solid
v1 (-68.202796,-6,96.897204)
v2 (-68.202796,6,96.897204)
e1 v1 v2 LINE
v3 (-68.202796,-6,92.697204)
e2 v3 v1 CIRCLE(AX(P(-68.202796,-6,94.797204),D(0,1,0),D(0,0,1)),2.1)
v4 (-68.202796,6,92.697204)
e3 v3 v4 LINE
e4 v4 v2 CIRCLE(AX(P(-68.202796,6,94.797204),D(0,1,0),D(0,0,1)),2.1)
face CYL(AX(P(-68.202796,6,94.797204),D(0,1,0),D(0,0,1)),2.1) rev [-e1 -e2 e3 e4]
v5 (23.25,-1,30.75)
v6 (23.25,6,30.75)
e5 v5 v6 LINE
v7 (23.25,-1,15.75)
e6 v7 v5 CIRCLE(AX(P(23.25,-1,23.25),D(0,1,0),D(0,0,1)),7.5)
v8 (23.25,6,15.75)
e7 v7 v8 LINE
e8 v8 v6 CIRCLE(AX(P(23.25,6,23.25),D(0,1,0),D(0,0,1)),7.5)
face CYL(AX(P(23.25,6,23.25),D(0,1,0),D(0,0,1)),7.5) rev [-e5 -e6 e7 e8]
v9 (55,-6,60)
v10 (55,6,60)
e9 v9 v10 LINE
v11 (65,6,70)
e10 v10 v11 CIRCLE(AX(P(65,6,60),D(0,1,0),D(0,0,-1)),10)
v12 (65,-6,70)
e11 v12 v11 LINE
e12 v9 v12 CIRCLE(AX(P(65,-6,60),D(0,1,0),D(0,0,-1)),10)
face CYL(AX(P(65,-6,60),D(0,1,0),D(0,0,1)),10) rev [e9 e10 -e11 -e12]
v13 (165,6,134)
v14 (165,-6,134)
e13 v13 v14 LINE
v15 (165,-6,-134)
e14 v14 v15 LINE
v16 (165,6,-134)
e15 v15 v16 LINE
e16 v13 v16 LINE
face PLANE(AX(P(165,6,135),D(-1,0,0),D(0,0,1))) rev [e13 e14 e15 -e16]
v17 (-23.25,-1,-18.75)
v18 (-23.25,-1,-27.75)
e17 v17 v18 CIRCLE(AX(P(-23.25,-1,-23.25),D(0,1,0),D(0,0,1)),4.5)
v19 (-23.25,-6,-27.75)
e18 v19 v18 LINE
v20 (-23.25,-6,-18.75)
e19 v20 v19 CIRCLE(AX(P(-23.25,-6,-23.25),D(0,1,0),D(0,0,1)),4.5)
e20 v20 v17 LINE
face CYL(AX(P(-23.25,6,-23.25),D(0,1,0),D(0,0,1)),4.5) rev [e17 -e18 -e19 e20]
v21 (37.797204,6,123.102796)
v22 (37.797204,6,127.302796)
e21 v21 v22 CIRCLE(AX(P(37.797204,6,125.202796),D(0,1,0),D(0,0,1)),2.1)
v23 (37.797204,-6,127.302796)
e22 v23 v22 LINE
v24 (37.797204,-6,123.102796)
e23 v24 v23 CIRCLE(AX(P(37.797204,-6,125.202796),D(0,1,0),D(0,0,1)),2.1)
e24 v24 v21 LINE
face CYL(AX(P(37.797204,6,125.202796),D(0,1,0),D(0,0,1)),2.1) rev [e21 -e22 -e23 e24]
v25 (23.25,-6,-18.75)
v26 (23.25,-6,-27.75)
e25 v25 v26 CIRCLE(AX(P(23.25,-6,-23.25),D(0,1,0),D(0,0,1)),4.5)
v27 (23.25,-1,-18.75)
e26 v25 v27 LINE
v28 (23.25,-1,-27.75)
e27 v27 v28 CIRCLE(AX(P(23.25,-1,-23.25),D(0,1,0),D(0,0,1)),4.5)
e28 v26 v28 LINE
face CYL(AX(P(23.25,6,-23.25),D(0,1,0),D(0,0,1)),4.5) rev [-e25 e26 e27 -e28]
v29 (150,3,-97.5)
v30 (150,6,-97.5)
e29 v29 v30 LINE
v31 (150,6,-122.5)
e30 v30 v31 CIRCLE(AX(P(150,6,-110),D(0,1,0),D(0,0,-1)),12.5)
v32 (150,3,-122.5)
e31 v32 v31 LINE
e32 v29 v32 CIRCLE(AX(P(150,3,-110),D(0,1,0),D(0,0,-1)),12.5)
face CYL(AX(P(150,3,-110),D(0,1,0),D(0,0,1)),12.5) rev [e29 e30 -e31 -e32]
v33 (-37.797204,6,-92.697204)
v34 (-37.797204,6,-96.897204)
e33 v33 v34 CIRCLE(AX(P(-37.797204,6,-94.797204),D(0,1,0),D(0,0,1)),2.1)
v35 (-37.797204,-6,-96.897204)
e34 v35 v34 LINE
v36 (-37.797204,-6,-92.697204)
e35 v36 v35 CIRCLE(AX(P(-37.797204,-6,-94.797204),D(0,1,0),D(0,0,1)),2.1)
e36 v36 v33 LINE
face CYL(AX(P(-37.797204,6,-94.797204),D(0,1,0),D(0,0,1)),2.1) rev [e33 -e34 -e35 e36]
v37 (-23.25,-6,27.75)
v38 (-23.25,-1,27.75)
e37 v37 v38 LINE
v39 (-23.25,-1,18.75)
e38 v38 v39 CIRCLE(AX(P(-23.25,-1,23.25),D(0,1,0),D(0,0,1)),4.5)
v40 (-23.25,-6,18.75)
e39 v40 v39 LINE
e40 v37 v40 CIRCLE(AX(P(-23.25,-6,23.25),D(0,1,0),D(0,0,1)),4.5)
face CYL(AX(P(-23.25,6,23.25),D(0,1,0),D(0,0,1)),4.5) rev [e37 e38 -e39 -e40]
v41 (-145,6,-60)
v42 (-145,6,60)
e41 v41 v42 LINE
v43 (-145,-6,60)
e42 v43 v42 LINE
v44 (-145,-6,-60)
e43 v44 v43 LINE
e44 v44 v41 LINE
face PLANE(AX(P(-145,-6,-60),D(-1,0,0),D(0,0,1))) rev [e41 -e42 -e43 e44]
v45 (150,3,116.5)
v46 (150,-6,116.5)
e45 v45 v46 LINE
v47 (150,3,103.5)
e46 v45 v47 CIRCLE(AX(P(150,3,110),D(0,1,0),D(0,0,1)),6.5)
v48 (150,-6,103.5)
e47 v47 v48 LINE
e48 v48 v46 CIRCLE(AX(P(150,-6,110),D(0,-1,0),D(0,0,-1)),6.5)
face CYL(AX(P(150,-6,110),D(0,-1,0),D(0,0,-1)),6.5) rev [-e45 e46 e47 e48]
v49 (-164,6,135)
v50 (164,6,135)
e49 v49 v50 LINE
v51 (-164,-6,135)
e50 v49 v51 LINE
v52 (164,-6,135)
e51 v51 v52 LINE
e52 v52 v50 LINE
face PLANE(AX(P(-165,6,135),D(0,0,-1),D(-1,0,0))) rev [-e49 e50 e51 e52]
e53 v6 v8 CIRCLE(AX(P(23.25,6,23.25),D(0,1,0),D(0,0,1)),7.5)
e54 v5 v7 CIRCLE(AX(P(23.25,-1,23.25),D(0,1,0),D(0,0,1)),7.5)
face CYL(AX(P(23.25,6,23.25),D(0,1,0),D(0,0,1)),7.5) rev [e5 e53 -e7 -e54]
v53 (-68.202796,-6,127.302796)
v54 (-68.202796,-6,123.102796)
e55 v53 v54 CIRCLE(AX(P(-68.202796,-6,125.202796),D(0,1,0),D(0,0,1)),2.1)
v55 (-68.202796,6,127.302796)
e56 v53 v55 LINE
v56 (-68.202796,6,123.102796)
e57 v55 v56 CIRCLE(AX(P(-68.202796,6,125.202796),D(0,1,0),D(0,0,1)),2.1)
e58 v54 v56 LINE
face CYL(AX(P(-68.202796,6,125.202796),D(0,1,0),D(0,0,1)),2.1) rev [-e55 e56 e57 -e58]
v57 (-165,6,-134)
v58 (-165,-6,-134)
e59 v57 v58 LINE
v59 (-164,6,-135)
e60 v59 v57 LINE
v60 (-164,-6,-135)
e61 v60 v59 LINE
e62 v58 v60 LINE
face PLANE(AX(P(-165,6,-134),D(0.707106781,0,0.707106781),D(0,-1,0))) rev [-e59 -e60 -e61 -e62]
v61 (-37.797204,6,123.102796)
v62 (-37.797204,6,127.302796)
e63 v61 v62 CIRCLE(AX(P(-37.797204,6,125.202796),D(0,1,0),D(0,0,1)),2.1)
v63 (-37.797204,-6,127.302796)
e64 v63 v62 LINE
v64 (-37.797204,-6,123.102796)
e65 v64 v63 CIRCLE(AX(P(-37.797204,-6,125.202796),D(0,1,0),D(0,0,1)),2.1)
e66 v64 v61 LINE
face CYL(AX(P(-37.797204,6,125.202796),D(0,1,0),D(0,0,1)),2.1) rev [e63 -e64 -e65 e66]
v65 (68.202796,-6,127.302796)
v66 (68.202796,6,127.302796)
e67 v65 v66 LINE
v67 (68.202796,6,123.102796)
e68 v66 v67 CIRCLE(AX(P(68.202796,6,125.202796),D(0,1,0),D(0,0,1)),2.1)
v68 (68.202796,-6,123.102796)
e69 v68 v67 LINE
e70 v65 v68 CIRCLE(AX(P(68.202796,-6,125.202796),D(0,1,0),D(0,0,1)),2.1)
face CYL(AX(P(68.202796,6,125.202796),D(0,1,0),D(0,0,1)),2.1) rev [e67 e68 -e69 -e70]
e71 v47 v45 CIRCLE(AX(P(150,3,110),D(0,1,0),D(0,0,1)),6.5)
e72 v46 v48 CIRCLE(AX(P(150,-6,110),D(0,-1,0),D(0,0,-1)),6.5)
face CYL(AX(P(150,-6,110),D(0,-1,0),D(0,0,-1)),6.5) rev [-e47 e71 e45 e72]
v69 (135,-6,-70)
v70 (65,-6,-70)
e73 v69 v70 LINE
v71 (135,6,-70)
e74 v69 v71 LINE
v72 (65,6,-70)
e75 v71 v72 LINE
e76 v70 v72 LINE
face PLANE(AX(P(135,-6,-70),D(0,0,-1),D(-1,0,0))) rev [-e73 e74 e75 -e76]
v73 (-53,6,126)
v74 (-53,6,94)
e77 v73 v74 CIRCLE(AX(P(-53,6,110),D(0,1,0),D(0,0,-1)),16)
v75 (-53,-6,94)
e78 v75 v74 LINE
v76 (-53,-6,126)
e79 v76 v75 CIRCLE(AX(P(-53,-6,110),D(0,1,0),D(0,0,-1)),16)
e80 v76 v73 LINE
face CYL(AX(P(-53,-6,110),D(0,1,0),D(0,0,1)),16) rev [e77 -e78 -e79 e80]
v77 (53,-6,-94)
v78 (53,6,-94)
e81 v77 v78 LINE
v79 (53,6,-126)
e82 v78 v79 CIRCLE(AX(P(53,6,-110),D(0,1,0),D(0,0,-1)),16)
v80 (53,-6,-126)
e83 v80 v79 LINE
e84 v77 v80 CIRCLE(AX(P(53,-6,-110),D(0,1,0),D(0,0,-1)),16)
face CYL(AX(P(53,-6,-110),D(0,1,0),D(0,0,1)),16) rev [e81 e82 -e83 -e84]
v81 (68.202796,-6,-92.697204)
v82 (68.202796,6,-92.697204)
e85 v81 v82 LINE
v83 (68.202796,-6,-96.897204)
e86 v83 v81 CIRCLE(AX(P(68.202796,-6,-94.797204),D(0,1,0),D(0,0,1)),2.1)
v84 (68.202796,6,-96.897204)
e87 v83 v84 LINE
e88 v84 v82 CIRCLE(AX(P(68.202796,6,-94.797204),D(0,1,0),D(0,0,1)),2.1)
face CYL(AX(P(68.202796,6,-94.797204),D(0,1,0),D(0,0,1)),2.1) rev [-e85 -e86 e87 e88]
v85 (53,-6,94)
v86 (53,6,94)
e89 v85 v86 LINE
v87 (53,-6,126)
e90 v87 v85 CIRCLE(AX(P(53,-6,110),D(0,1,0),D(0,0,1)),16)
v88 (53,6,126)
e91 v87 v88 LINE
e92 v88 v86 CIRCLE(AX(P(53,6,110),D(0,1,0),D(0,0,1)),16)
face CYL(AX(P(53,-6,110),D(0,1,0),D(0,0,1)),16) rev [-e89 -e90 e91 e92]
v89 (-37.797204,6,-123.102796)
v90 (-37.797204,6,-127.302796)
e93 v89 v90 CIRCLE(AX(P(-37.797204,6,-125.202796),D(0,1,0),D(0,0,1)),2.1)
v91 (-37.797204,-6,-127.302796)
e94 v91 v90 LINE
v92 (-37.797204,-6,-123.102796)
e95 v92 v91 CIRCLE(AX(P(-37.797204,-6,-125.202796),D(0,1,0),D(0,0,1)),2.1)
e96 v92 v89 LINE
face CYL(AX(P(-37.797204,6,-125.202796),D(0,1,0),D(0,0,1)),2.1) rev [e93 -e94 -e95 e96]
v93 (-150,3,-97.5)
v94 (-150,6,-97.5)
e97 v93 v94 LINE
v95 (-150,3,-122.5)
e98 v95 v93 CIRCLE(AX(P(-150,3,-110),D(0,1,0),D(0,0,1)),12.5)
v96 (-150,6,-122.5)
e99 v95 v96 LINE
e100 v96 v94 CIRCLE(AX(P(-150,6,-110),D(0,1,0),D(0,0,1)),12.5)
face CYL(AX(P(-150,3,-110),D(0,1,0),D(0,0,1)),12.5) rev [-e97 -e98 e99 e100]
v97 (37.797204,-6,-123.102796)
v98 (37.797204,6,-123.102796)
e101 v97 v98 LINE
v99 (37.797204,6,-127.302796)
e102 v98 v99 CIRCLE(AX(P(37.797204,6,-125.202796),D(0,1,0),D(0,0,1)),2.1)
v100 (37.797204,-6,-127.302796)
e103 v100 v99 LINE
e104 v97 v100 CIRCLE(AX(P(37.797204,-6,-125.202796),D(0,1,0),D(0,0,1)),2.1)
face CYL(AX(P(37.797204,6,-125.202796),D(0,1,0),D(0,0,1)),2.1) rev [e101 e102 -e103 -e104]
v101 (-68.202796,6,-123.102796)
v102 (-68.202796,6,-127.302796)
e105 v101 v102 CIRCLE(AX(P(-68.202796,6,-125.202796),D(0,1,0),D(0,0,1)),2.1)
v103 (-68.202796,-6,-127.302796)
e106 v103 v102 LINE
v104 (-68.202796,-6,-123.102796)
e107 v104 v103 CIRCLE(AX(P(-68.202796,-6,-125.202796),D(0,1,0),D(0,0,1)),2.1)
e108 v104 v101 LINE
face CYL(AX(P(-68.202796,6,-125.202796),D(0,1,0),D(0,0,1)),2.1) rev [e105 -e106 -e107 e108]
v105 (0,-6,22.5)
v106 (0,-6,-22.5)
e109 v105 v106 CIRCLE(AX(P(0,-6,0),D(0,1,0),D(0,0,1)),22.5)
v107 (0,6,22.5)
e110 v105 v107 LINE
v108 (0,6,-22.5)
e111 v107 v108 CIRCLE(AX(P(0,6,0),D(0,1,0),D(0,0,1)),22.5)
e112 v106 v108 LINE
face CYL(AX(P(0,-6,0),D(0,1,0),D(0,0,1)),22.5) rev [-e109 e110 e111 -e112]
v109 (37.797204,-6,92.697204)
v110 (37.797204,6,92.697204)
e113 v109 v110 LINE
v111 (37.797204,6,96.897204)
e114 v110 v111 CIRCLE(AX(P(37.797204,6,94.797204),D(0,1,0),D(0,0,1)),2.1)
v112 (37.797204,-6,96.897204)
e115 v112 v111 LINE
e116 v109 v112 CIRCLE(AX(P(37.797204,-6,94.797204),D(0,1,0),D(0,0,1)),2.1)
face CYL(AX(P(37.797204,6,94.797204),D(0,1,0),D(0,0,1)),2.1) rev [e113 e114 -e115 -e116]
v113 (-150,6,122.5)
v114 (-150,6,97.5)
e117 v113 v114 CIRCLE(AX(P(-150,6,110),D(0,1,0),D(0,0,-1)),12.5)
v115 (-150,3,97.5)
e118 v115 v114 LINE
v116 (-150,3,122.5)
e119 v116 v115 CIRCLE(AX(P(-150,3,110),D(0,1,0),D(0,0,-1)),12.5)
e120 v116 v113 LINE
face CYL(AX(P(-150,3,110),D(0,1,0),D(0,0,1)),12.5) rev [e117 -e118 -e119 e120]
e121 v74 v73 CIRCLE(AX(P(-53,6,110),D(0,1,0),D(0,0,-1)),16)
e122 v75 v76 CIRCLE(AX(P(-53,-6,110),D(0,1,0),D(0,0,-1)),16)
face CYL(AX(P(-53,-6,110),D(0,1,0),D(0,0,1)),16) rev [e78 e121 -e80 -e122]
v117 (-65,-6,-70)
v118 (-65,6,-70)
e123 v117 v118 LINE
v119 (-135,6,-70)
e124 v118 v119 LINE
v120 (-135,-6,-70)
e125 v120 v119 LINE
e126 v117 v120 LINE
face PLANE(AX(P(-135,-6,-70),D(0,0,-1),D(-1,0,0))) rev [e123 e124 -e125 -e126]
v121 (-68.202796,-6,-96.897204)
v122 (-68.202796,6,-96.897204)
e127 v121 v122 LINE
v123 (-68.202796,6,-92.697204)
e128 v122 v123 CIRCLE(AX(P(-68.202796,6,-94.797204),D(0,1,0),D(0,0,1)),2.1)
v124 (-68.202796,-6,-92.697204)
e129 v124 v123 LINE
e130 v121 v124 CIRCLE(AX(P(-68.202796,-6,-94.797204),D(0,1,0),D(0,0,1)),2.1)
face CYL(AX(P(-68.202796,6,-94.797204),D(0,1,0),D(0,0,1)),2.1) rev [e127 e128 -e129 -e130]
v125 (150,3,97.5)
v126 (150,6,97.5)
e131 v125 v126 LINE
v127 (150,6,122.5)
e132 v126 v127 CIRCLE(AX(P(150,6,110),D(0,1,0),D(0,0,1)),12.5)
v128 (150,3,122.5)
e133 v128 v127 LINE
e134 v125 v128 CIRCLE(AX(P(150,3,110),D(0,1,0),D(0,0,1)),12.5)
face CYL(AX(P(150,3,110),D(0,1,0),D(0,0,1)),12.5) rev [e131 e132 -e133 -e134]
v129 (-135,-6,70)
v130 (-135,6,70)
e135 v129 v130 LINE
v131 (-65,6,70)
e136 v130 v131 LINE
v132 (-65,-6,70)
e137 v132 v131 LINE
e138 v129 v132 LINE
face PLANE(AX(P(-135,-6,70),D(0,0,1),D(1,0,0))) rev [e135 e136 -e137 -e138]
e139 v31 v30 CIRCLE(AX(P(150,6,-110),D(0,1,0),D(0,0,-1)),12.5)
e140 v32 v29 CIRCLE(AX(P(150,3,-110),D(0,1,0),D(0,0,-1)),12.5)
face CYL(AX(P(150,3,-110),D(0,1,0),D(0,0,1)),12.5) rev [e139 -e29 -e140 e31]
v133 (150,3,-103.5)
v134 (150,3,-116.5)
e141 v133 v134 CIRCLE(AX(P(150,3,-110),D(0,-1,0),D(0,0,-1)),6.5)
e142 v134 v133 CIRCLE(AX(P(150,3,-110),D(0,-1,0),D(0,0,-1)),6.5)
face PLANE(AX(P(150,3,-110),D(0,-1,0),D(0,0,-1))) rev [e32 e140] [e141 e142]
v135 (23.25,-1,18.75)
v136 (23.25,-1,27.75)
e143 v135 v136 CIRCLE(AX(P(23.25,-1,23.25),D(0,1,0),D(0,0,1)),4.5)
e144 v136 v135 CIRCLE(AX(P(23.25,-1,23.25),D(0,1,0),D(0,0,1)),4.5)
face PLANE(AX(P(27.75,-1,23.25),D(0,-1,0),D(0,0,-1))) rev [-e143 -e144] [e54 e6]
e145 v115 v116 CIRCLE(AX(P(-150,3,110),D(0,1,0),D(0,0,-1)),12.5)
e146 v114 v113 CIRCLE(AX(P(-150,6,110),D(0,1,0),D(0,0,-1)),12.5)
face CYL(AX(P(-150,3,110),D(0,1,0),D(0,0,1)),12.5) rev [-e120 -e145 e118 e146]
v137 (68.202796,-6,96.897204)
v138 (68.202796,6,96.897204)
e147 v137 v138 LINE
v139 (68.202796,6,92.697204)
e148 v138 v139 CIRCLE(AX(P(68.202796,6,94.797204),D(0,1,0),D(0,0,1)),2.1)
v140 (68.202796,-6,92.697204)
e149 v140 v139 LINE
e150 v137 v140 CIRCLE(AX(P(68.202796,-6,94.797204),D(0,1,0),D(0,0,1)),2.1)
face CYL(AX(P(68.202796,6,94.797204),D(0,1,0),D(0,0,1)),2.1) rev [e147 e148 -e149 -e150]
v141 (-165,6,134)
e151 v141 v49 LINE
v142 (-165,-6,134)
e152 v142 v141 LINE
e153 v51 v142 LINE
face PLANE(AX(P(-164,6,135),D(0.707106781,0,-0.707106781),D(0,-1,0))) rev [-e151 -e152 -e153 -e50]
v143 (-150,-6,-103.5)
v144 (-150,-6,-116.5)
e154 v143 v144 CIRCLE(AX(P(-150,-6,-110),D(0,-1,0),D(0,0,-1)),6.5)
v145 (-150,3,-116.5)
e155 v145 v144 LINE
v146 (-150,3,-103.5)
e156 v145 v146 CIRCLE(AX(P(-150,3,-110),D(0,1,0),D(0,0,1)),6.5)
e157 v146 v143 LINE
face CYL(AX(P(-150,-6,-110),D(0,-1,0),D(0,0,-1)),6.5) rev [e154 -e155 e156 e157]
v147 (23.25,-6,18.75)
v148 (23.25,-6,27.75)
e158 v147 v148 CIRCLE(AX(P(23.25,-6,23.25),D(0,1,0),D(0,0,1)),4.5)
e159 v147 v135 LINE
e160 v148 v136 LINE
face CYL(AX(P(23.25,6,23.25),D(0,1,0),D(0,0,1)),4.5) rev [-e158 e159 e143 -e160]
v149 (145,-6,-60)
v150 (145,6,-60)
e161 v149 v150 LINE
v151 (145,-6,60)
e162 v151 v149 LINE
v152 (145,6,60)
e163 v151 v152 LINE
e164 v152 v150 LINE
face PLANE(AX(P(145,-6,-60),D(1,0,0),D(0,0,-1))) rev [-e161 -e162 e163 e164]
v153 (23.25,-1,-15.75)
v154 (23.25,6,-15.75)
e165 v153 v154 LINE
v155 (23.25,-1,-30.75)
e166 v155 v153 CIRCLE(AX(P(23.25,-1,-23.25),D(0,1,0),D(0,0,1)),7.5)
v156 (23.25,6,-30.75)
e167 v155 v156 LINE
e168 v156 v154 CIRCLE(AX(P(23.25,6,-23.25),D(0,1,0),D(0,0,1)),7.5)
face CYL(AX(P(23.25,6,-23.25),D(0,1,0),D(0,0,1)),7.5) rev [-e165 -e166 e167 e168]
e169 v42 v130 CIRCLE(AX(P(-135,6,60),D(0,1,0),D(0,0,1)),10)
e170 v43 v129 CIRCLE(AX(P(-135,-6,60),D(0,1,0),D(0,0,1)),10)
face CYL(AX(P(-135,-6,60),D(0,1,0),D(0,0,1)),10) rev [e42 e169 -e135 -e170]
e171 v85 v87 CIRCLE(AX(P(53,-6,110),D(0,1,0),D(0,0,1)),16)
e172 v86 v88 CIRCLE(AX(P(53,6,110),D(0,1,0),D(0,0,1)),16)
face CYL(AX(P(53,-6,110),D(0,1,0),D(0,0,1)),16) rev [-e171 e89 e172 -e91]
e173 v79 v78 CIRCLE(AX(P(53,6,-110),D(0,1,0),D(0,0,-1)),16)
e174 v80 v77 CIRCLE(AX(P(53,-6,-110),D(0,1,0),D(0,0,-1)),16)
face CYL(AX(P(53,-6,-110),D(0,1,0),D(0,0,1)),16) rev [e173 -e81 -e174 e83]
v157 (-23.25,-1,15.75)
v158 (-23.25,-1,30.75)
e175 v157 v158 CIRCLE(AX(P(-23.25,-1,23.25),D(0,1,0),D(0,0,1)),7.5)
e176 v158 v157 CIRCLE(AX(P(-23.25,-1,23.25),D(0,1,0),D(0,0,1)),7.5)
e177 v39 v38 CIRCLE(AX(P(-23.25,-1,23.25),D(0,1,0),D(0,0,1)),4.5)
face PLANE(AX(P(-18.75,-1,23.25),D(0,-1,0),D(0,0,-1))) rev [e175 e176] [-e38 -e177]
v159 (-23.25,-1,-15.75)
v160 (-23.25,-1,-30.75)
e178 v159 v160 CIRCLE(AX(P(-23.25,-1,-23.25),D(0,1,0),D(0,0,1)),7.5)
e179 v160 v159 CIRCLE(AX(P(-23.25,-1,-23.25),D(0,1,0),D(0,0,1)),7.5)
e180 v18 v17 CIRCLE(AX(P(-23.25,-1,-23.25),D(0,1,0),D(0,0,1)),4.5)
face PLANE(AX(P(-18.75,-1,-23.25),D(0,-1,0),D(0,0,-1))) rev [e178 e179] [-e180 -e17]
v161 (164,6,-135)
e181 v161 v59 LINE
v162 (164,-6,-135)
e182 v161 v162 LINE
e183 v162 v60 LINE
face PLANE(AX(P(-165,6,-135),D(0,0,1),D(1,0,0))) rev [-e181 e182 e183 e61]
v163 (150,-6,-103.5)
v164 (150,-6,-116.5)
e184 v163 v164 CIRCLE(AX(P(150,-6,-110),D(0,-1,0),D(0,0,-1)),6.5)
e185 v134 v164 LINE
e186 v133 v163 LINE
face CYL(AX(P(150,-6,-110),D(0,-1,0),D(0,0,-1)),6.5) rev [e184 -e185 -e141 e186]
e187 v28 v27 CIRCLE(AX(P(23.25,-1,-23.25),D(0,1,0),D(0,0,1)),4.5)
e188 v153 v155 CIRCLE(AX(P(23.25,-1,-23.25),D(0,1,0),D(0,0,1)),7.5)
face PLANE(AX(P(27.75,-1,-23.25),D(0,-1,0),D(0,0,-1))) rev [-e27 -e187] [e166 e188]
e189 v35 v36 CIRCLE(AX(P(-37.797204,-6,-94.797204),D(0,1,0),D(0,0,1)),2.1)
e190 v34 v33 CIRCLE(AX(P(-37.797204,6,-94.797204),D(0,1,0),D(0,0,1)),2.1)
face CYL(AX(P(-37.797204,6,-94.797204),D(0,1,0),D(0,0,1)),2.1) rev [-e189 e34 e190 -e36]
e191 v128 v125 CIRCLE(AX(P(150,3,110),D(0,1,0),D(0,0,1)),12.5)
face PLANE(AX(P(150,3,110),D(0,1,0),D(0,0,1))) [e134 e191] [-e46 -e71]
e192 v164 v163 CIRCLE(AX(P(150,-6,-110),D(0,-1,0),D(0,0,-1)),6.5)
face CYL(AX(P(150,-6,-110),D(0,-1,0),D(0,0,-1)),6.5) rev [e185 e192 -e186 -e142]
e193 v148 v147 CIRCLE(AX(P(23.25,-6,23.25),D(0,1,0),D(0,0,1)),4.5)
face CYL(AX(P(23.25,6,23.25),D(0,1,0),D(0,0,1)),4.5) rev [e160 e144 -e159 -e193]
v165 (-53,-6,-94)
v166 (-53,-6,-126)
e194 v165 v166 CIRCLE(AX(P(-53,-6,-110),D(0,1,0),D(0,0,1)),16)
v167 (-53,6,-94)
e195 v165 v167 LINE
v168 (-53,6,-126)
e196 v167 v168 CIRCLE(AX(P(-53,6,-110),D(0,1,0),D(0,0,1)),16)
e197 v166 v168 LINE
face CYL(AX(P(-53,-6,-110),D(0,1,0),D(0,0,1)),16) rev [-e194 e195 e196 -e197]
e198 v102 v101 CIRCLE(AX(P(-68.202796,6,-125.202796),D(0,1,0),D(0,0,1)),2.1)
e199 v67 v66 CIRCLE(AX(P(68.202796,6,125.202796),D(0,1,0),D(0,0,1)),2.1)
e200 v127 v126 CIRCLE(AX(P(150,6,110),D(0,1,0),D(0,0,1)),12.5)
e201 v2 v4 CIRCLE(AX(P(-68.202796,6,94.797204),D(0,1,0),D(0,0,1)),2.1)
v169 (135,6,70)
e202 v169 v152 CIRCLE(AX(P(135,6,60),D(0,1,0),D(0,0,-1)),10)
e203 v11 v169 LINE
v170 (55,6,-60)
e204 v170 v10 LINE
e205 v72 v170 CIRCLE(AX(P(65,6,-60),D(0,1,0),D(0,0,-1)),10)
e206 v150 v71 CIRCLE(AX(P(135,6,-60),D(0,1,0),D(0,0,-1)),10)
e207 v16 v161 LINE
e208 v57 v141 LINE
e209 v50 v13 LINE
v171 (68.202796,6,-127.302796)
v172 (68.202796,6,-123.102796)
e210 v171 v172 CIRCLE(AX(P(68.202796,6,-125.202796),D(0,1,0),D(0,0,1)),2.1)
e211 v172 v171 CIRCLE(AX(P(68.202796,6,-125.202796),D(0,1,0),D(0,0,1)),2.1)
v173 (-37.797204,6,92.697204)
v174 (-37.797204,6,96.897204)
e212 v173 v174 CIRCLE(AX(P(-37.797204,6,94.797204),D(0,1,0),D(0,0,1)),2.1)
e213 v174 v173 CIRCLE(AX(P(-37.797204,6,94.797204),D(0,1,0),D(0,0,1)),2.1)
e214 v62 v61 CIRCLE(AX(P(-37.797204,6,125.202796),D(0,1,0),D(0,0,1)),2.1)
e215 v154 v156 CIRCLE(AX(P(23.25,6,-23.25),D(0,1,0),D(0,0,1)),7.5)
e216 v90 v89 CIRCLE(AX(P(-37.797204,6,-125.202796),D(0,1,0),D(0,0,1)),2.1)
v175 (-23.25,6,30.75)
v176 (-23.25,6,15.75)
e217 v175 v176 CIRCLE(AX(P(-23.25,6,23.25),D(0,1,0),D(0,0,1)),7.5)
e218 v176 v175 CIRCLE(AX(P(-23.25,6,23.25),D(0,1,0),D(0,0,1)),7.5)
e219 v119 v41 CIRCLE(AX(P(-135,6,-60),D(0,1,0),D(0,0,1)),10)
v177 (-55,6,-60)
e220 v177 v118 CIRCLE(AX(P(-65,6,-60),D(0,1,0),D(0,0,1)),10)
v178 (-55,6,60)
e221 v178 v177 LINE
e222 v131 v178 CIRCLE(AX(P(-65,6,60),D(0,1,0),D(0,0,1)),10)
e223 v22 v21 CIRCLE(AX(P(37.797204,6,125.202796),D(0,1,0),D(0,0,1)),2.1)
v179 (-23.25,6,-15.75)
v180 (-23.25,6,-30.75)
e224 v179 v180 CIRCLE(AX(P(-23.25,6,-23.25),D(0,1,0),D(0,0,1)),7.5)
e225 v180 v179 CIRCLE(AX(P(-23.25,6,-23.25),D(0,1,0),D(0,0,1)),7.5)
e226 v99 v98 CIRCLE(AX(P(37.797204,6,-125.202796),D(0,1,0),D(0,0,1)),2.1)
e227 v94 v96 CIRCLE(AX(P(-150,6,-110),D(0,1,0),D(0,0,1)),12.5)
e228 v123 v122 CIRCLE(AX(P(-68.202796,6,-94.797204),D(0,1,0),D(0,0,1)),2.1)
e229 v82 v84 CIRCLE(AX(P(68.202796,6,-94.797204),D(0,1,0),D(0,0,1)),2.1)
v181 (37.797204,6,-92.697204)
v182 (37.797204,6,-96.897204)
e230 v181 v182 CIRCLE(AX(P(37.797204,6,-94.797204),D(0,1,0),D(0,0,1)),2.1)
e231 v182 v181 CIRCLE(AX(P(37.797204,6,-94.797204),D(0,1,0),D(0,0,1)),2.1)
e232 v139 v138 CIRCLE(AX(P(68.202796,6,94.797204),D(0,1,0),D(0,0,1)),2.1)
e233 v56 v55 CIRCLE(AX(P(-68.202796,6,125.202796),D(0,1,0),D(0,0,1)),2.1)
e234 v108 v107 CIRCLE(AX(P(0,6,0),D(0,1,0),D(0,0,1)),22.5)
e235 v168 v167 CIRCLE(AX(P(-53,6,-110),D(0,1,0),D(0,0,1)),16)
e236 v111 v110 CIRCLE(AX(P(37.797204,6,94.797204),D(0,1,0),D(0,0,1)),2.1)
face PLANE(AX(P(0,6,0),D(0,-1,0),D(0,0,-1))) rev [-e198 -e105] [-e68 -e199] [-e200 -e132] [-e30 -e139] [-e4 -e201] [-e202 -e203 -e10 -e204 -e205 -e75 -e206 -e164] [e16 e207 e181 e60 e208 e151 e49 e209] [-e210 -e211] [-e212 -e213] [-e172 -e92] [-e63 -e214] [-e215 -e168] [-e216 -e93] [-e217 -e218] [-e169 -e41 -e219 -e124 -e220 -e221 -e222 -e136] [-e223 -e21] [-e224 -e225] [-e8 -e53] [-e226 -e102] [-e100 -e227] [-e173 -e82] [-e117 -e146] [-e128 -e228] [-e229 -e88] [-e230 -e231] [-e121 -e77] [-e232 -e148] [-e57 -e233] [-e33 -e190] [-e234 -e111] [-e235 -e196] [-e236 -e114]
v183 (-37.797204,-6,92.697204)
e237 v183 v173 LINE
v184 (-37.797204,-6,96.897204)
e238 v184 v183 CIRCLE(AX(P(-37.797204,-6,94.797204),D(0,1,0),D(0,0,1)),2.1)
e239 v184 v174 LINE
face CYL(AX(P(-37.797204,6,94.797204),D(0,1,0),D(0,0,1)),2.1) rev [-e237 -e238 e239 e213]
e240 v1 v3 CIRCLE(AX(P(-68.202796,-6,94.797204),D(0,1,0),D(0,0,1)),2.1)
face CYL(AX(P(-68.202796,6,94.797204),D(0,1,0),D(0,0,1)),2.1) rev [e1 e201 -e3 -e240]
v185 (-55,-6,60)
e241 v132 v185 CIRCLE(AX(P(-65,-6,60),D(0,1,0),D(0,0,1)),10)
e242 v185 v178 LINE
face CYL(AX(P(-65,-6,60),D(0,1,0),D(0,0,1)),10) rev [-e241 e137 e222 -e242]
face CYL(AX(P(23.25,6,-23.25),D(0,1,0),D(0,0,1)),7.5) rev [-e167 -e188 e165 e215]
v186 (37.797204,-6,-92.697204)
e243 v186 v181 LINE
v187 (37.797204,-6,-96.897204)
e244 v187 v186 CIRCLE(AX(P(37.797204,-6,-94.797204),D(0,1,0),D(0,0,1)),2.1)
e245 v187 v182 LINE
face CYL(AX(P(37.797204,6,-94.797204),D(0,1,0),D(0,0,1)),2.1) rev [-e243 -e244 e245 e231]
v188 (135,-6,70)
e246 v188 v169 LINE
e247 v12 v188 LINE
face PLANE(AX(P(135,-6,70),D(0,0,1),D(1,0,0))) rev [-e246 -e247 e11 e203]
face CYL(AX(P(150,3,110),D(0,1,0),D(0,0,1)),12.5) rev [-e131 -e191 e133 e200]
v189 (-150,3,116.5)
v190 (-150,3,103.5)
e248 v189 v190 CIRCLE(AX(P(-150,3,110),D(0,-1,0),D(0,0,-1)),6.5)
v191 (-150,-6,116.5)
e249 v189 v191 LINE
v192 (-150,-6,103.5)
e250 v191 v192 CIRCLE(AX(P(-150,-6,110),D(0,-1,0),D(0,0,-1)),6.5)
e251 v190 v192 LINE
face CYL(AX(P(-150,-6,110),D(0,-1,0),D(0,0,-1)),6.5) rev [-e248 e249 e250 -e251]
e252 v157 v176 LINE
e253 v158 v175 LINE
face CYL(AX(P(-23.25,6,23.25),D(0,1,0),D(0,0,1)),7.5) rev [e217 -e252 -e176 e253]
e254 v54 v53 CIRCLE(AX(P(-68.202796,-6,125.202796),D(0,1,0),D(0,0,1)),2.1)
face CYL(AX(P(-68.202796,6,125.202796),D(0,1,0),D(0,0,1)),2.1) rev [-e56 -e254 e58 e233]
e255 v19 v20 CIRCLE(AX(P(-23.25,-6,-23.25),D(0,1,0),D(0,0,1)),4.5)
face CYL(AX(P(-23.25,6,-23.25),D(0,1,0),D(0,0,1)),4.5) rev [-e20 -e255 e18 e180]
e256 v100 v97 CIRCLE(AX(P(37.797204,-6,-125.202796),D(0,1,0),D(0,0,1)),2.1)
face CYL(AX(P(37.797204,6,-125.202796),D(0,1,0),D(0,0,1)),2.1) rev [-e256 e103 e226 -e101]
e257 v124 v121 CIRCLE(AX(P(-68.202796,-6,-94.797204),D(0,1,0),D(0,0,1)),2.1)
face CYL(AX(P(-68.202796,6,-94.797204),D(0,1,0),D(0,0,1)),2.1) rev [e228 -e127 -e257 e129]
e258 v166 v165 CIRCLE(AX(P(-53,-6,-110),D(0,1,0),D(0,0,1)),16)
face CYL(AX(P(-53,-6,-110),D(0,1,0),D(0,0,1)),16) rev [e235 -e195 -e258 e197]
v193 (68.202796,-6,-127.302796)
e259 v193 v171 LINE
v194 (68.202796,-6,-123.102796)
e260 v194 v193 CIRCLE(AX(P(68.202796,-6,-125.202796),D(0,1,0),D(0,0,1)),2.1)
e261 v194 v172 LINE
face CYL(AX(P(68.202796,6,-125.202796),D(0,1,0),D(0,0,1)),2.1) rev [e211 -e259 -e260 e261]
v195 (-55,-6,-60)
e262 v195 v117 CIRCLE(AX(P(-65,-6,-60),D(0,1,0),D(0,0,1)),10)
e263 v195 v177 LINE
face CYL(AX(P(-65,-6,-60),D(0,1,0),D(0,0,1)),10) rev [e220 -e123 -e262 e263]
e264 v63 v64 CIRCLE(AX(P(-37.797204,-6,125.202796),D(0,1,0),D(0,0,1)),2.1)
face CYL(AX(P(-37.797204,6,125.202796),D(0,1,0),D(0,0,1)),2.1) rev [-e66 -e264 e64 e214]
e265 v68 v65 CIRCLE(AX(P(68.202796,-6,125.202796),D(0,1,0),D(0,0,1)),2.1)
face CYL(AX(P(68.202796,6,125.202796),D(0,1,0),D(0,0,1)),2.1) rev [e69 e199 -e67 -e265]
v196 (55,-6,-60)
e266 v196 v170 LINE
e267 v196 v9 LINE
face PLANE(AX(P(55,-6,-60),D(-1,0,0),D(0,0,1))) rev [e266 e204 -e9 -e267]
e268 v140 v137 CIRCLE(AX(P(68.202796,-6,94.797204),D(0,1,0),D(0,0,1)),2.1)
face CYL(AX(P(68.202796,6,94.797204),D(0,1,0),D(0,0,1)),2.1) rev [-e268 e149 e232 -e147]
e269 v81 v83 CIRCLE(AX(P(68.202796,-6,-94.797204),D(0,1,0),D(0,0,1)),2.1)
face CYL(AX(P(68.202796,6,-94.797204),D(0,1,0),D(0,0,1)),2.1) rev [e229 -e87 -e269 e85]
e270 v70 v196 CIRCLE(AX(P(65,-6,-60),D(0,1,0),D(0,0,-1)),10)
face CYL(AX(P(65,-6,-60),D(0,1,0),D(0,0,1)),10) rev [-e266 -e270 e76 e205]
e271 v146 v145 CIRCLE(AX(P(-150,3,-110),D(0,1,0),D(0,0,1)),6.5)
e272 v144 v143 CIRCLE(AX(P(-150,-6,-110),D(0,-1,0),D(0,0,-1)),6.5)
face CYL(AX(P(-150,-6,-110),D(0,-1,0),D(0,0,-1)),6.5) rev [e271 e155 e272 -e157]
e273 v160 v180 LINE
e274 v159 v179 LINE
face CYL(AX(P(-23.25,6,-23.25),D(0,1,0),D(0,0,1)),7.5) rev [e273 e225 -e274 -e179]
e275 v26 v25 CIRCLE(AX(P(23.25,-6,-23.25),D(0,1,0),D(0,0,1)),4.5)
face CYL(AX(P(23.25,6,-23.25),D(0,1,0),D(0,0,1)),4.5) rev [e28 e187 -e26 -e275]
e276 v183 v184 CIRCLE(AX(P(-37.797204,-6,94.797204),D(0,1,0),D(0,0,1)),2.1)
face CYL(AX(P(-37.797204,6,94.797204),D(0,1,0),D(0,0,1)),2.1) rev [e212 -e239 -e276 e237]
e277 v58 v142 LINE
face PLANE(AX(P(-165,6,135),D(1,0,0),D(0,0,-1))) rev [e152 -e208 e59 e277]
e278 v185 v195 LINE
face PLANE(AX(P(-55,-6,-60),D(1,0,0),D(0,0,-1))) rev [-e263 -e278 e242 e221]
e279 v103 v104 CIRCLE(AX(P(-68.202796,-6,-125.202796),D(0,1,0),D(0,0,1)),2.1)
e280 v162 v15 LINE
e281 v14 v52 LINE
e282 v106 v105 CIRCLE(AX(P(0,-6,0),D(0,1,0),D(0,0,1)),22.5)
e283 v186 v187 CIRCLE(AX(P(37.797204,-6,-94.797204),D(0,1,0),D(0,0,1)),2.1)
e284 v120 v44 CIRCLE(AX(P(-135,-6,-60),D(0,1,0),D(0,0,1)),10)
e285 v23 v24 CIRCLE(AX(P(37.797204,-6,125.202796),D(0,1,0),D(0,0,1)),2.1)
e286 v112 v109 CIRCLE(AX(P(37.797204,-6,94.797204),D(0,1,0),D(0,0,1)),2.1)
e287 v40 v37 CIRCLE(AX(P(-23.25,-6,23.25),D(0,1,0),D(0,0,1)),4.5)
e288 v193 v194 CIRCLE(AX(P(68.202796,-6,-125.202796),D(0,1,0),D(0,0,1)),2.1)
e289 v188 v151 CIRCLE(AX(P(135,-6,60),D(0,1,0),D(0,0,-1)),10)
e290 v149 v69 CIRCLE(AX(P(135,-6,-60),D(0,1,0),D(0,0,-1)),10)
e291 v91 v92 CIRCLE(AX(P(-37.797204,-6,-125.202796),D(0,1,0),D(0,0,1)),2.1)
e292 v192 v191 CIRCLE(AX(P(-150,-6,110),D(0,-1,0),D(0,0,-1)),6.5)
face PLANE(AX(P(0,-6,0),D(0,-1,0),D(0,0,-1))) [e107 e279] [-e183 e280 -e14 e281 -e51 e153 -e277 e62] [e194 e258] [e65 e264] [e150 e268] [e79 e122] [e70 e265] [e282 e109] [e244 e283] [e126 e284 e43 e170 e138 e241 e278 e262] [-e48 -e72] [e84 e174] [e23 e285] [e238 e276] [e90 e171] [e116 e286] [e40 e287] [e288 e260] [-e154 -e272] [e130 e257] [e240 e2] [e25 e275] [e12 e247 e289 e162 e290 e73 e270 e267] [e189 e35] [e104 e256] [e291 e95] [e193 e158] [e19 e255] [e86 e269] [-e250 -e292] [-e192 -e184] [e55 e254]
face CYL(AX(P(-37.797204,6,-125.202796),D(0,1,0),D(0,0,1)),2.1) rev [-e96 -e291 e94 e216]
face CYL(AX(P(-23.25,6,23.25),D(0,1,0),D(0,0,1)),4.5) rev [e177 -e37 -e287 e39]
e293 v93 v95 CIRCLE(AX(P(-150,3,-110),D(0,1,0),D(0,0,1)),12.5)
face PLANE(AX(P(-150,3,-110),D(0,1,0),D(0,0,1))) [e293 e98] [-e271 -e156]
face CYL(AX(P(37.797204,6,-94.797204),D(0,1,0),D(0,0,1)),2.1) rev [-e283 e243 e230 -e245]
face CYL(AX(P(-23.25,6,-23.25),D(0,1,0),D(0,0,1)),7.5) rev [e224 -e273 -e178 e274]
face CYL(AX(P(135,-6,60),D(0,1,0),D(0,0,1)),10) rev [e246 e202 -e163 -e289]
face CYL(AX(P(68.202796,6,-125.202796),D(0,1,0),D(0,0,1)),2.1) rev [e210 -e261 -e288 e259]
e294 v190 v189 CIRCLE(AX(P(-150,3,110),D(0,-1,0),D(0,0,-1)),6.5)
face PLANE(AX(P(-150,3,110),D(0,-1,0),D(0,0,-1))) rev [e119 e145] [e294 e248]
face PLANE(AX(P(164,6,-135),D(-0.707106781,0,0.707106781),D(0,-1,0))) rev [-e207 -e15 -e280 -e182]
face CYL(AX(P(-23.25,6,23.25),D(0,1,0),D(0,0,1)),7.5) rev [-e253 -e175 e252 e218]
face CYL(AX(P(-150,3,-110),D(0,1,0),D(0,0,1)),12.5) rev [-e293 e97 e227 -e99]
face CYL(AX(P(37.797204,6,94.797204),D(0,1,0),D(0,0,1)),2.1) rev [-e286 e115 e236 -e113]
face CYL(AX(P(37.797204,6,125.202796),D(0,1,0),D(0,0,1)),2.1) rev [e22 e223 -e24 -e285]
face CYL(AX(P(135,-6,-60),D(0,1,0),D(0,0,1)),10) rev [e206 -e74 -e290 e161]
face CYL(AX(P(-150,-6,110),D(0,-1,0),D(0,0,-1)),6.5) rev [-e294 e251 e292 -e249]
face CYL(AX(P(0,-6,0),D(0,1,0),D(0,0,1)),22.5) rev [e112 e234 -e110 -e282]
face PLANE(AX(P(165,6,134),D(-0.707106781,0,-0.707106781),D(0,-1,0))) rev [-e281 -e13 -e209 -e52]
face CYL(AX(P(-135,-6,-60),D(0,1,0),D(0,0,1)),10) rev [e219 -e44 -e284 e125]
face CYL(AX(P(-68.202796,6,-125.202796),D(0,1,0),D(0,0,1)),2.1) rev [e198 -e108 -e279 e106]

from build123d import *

# Parameters (mm, degrees)
SKETCH1_W                                            = 330
SKETCH1_H                                            = 270
BOSS_EXTRUDE1_DEPTH                                  = 6
SKETCH2_R                                            = 16
CUT_EXTRUDE1_DEPTH                                   = 214.527515791
SKETCH3_R                                            = 22.5
CUT_EXTRUDE2_DEPTH                                   = 214.527515791
SKETCH4_R                                            = 12.5
CUT_EXTRUDE3_DEPTH                                   = 3
M12_CLEARANCE_HOLE1_D                                = 13
M5_TAPPED_HOLE1_D                                    = 4.2
HOLE_SIZE_PER_SOCKET_HEAD_CAP_SCREW_TYPE_D           = 9
HOLE_SIZE_PER_SOCKET_HEAD_CAP_SCREW_TYPE_CBORE_D     = 15
HOLE_SIZE_PER_SOCKET_HEAD_CAP_SCREW_TYPE_CBORE_DEPTH = 7
CHAMFER1_SIZE                                        = 1
CUT_EXTRUDE4_DEPTH                                   = 214.527515791


with BuildPart() as part:
    # Sketch1 → Boss-Extrude1 (new, symmetric)
    with BuildSketch(Plane(origin=(0, 0, 0), x_dir=(1, 0, 0), z_dir=(0, 1, 0))):
        Rectangle(SKETCH1_W, SKETCH1_H)
    extrude(amount=BOSS_EXTRUDE1_DEPTH, both=True)

    # Sketch2 → Cut-Extrude1 (cut, through all)
    with BuildSketch(Plane(origin=(0, 6, 0), x_dir=(1, 0, 0), z_dir=(0, 1, 0))):
        with Locations(Location((-53, 110, 0), (0, 0, 270))):
            Circle(SKETCH2_R)
        with Locations(Location((53, 110, 0), (0, 0, 90))):
            Circle(SKETCH2_R)
        with Locations(Location((53, -110, 0), (0, 0, 270))):
            Circle(SKETCH2_R)
        with Locations(Location((-53, -110, 0), (0, 0, 90))):
            Circle(SKETCH2_R)
    extrude(amount=-CUT_EXTRUDE1_DEPTH, mode=Mode.SUBTRACT)

    # Sketch3 → Cut-Extrude2 (cut, through all)
    with BuildSketch(Plane(origin=(0, 6, 0), x_dir=(1, 0, 0), z_dir=(0, 1, 0))):
        with Locations(Location((0, 0, 0), (0, 0, 270))):
            Circle(SKETCH3_R)
    extrude(amount=-CUT_EXTRUDE2_DEPTH, mode=Mode.SUBTRACT)

    # Sketch4 → Cut-Extrude3 (cut)
    with BuildSketch(Plane(origin=(0, 6, 0), x_dir=(1, 0, 0), z_dir=(0, 1, 0))):
        with Locations(Location((-150, 110, 0), (0, 0, 270))):
            Circle(SKETCH4_R)
        with Locations(Location((150, 110, 0), (0, 0, 90))):
            Circle(SKETCH4_R)
        with Locations(Location((150, -110, 0), (0, 0, 270))):
            Circle(SKETCH4_R)
        with Locations(Location((-150, -110, 0), (0, 0, 90))):
            Circle(SKETCH4_R)
    extrude(amount=-CUT_EXTRUDE3_DEPTH, mode=Mode.SUBTRACT)

    # M12 Clearance Hole1 (through all)
    with Locations(Plane(origin=(0, -6, 0), x_dir=(-1, 0, 0), z_dir=(0, -1, 0))):
        with Locations((150, -110), (-150, -110), (150, 110), (-150, 110)):
            Hole(M12_CLEARANCE_HOLE1_D / 2)

    # M5 Tapped Hole1 (through all)
    with Locations(Plane(origin=(0, 6, 0), x_dir=(1, 0, 0), z_dir=(0, 1, 0))):
        with Locations((-68.202795796, -125.202795796), (-68.202795796, 125.202795796), (-37.797204204, 125.202795796), (-37.797204204, 94.797204204), (-68.202795796, 94.797204204), (37.797204204, 125.202795796), (37.797204204, 94.797204204), (68.202795796, 94.797204204), (68.202795796, 125.202795796), (68.202795796, -125.202795796), (68.202795796, -94.797204204), (37.797204204, -94.797204204), (37.797204204, -125.202795796), (-37.797204204, -125.202795796), (-37.797204204, -94.797204204), (-68.202795796, -94.797204204)):
            Hole(M5_TAPPED_HOLE1_D / 2)

    # Hole size per socket head cap screw type 1 (through all)
    with Locations(Plane(origin=(0, 6, 0), x_dir=(1, 0, 0), z_dir=(0, 1, 0))):
        with Locations((0, 0), (23.25, 23.25), (-23.25, -23.25), (-23.25, 23.25), (23.25, -23.25)):
            CounterBoreHole(HOLE_SIZE_PER_SOCKET_HEAD_CAP_SCREW_TYPE_D / 2, HOLE_SIZE_PER_SOCKET_HEAD_CAP_SCREW_TYPE_CBORE_D / 2, HOLE_SIZE_PER_SOCKET_HEAD_CAP_SCREW_TYPE_CBORE_DEPTH)

    # Chamfer1
    chamfer1_edges = [part.edges().sort_by_distance(p)[0] for p in [
        (165, 0, 135),
        (-165, 0, 135),
        (-165, 0, -135),
        (165, 0, -135),
    ]]
    chamfer(chamfer1_edges, length=CHAMFER1_SIZE)

    # Sketch11 → Cut-Extrude4 (cut, through all)
    with BuildSketch(Plane(origin=(0, 6, 0), x_dir=(1, 0, 0), z_dir=(0, 1, 0))):
        with BuildLine():
            Line((-135, 70), (-65, 70))
            ThreePointArc((-65, 70), (-57.928932188, 67.071067812), (-55, 60))
            Line((-55, 60), (-55, -60))
            ThreePointArc((-55, -60), (-57.928932188, -67.071067812), (-65, -70))
            Line((-65, -70), (-135, -70))
            ThreePointArc((-135, -70), (-142.071067812, -67.071067812), (-145, -60))
            Line((-145, -60), (-145, 60))
            ThreePointArc((-145, 60), (-142.071067812, 67.071067812), (-135, 70))
        make_face()
        with BuildLine():
            Line((55, 60), (55, -60))
            ThreePointArc((55, -60), (57.928932188, -67.071067812), (65, -70))
            Line((65, -70), (135, -70))
            ThreePointArc((135, -70), (142.071067812, -67.071067812), (145, -60))
            Line((145, -60), (145, 60))
            ThreePointArc((145, 60), (142.071067812, 67.071067812), (135, 70))
            Line((135, 70), (65, 70))
            ThreePointArc((65, 70), (57.928932188, 67.071067812), (55, 60))
        make_face()
    extrude(amount=-CUT_EXTRUDE4_DEPTH, mode=Mode.SUBTRACT)


solid = part.part
